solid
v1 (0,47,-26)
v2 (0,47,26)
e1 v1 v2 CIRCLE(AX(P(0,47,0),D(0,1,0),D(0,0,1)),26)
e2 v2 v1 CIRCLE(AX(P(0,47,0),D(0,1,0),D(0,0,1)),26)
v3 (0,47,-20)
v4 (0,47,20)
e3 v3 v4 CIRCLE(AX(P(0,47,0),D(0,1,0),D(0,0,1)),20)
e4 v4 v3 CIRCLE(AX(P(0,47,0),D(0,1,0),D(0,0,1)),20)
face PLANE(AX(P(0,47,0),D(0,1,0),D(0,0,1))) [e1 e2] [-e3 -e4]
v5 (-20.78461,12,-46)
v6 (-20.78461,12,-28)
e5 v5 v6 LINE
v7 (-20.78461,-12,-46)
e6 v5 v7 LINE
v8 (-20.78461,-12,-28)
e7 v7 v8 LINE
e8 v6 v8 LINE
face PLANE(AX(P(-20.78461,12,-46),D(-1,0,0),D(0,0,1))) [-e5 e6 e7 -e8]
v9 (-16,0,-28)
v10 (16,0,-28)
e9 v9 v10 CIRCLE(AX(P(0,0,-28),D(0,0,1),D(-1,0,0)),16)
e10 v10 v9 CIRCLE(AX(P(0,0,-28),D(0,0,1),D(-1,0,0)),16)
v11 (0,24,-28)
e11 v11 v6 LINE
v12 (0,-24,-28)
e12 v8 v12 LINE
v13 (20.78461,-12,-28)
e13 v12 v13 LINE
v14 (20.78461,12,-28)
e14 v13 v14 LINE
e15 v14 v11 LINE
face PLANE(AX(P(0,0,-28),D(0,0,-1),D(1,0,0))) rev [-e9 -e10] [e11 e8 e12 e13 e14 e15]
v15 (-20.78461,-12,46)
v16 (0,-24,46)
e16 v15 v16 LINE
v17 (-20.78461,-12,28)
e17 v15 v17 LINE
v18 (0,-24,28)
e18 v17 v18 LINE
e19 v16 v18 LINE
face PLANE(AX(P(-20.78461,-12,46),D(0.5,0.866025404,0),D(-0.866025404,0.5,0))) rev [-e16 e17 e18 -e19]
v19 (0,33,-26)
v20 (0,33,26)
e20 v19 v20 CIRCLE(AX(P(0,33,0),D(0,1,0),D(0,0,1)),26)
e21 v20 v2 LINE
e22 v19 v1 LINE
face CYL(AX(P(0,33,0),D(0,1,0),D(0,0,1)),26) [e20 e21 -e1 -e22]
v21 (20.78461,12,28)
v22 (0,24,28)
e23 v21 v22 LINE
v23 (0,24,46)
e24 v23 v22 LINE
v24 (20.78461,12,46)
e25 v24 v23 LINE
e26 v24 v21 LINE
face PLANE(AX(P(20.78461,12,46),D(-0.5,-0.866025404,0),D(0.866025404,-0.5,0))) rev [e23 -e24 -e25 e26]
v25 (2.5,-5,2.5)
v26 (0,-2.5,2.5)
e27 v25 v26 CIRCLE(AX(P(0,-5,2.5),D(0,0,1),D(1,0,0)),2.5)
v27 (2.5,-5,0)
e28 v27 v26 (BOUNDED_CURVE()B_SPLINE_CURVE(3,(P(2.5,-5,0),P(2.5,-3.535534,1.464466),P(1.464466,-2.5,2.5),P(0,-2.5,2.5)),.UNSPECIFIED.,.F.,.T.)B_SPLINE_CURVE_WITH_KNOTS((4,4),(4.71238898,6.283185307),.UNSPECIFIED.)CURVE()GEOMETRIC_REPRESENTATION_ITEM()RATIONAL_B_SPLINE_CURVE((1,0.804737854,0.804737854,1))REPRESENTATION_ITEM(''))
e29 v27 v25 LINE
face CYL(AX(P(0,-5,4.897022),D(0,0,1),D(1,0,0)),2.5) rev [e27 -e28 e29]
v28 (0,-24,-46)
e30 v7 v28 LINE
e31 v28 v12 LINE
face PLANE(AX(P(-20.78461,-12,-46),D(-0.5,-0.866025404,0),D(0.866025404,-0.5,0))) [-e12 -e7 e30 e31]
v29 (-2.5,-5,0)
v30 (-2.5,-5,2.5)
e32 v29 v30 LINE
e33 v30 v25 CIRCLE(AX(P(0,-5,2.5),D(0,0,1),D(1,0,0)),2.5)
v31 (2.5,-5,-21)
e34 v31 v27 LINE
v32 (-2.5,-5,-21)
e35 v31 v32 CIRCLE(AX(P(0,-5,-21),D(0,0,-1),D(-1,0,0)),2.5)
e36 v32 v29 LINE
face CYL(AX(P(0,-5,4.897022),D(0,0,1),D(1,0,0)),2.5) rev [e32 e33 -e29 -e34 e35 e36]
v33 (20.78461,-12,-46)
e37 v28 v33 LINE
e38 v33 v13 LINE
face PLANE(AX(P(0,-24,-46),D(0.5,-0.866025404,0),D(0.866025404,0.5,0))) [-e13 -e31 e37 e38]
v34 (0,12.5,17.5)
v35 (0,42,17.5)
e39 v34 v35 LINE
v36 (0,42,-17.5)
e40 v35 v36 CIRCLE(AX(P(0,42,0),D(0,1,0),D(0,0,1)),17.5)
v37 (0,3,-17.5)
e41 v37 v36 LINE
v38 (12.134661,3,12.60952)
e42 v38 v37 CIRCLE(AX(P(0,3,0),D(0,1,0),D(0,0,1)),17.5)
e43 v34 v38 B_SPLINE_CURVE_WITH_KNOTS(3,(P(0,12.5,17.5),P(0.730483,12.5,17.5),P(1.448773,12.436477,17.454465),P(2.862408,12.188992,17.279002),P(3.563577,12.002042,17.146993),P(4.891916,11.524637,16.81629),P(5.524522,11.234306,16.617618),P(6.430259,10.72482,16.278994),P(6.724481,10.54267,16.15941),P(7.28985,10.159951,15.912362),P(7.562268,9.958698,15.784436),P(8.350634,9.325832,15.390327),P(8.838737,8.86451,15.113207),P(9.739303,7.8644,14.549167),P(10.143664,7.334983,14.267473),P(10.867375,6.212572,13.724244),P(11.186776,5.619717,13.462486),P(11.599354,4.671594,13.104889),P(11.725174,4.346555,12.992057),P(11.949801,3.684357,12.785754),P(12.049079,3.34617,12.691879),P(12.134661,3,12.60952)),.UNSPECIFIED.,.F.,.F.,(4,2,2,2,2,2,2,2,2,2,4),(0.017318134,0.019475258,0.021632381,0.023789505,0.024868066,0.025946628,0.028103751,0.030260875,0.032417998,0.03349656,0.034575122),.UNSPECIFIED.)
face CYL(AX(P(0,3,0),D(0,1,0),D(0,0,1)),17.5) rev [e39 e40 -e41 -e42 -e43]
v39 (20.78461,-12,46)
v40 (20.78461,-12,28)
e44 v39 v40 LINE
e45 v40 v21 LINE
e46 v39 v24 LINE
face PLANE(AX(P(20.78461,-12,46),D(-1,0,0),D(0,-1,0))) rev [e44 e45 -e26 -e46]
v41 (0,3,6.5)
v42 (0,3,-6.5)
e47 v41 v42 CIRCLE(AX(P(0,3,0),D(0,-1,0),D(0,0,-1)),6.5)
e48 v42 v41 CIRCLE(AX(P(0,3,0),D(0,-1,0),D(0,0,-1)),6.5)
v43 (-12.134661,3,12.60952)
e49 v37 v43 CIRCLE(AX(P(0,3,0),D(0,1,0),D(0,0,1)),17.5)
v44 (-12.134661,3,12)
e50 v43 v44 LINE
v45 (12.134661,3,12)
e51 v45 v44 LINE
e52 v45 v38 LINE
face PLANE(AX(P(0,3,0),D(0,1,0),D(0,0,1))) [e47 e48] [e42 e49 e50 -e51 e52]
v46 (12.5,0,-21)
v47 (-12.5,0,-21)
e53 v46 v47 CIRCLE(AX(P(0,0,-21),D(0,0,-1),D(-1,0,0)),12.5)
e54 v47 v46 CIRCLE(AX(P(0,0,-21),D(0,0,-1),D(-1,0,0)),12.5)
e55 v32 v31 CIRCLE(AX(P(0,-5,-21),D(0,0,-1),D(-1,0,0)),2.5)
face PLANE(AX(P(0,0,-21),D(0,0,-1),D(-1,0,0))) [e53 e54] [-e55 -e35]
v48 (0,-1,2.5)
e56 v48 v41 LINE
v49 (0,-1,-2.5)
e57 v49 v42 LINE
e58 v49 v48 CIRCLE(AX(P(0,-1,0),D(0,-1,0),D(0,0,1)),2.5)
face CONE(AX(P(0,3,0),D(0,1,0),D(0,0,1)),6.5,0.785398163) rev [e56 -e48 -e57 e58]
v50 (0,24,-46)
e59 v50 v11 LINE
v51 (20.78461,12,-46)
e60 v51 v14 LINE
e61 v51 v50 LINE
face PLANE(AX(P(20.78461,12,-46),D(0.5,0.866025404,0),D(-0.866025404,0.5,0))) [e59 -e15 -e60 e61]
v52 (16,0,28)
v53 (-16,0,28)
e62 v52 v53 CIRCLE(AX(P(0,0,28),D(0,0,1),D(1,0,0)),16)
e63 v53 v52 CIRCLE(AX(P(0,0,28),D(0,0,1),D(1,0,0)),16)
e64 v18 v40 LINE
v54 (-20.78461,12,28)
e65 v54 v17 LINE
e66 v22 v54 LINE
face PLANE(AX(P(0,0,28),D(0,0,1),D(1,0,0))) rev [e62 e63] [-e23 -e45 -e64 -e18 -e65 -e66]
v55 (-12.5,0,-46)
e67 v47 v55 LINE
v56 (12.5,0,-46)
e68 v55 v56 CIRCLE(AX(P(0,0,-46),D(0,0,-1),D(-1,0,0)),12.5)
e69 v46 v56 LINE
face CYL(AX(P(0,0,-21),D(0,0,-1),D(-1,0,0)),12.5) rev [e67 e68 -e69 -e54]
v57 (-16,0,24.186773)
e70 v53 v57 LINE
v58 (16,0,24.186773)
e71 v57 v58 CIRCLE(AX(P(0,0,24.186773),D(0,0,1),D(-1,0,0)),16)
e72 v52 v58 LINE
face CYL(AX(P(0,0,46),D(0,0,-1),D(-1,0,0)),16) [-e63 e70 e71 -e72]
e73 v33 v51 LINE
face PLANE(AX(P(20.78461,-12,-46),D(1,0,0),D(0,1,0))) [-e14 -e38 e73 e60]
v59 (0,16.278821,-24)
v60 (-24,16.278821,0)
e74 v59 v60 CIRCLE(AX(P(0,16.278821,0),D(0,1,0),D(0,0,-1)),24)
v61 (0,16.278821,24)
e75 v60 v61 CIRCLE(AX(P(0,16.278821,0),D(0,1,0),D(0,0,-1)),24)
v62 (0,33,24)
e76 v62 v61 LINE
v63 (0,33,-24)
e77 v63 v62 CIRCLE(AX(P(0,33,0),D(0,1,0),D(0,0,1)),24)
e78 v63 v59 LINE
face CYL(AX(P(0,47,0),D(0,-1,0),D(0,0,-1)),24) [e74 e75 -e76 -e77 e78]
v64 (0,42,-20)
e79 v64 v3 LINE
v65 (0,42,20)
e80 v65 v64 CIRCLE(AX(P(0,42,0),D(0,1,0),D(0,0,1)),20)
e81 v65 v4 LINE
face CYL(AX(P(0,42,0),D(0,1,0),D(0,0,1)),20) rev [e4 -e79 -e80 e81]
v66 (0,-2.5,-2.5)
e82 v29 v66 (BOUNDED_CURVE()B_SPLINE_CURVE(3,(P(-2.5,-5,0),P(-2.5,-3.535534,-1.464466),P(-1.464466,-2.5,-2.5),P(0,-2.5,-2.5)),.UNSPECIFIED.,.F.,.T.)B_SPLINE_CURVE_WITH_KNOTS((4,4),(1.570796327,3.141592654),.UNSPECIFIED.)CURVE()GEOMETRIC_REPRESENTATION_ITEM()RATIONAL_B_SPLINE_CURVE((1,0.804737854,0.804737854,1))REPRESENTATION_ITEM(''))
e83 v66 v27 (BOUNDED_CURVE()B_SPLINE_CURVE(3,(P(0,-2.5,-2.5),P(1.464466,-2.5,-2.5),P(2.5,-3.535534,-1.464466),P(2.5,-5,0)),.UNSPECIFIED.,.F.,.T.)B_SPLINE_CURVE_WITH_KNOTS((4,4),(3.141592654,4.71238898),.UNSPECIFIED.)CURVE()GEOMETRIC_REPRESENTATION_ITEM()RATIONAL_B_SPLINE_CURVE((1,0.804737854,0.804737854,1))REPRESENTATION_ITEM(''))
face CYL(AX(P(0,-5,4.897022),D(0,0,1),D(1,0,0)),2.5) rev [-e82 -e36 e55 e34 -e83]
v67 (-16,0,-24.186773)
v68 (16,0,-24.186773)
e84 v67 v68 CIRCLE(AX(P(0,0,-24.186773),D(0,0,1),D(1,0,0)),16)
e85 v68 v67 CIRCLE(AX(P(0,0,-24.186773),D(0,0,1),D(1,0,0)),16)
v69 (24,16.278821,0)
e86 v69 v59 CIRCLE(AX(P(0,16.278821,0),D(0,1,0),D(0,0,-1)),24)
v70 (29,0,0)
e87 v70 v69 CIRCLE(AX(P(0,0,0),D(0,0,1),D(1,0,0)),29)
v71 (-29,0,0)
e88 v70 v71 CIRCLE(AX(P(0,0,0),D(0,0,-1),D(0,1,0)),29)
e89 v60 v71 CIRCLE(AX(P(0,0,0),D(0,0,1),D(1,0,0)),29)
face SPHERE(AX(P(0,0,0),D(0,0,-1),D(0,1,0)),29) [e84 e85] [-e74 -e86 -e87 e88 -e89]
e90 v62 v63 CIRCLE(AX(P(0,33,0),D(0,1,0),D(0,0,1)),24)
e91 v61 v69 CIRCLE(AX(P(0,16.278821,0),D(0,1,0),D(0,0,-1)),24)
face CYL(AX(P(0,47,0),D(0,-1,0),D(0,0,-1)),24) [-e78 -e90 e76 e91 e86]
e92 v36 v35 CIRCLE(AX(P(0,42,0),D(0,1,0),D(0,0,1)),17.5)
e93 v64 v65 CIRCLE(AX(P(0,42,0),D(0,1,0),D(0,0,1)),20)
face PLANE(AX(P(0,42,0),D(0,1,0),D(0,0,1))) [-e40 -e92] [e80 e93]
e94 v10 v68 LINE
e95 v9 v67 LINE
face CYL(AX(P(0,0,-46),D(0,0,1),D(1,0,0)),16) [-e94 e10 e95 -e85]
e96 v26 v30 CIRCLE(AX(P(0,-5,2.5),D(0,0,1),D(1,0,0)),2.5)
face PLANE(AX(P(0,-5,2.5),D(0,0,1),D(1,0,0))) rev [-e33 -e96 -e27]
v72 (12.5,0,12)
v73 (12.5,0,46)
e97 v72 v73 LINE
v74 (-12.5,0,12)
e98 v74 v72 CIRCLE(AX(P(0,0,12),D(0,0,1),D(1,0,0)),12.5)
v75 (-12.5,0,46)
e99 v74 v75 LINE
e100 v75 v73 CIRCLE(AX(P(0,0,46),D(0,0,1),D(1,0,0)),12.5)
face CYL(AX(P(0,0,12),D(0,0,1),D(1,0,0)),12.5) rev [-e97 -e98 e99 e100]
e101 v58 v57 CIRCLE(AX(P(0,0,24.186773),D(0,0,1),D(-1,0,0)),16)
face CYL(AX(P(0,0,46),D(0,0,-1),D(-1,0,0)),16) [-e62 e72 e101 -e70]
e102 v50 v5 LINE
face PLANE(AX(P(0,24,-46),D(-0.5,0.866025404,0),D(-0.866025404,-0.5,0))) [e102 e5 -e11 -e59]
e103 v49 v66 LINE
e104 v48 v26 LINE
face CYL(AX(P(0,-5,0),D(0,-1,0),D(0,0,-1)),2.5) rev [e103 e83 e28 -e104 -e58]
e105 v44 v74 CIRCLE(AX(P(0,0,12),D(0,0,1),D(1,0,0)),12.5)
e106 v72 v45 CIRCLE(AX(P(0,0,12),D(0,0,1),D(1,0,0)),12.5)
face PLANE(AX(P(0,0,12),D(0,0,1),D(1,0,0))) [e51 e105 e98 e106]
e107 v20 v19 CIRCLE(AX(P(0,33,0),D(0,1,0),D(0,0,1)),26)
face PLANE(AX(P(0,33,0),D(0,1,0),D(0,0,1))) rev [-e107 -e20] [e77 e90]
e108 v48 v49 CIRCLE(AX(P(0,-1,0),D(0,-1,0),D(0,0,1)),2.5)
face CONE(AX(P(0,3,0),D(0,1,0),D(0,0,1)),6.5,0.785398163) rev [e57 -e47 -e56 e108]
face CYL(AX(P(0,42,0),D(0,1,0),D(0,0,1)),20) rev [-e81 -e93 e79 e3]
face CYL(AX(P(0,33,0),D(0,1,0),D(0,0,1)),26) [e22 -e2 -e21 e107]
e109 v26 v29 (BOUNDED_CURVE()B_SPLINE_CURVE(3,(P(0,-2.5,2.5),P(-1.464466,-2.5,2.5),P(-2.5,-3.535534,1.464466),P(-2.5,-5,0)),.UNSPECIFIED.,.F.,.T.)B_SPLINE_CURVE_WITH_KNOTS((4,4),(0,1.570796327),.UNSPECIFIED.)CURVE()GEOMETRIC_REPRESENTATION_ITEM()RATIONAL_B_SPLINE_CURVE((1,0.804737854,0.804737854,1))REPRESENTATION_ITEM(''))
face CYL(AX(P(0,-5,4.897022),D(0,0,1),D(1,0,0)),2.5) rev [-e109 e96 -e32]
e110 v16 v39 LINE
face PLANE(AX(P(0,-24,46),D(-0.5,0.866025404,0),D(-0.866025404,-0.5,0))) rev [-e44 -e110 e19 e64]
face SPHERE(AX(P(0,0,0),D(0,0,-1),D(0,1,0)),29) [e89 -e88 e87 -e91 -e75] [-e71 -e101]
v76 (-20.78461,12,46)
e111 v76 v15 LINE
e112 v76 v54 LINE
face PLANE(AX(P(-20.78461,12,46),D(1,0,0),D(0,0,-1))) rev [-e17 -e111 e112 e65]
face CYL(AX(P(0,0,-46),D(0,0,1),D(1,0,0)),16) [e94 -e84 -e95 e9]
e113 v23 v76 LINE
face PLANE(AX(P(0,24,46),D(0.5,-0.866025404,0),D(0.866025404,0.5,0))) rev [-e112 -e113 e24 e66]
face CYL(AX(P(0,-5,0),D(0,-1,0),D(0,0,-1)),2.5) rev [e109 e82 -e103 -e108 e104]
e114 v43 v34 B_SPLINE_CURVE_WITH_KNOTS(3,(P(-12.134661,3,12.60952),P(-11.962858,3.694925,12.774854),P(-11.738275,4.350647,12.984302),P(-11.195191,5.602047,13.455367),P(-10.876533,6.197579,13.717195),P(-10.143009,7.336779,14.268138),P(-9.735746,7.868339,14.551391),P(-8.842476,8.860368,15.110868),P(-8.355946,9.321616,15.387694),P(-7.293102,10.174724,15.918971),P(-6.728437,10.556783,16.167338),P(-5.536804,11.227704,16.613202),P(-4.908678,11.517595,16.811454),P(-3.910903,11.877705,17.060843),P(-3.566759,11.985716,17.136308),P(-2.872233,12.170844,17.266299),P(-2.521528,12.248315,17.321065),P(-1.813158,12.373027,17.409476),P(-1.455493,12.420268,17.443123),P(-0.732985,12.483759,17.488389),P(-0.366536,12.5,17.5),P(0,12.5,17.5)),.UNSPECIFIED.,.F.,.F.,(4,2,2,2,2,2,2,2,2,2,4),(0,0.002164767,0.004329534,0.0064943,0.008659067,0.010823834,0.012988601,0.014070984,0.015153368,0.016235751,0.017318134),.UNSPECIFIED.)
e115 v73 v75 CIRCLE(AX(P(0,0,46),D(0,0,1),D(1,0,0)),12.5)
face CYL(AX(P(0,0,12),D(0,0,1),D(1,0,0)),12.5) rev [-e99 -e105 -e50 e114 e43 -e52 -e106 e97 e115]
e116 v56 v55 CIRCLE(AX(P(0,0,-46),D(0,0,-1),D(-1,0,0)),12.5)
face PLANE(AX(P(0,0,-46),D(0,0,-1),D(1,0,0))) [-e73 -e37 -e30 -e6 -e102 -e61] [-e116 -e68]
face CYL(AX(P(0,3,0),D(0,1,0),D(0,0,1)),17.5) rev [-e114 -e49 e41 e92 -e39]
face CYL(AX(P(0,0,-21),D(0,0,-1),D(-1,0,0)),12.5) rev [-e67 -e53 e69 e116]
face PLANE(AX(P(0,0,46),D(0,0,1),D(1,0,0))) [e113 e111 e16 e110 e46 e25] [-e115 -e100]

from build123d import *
from build123d.topology import SkipClean

# Parameters (mm, degrees)
SKETCH2_R           = 24
BOSS_EXTRUDE1_DEPTH = 47
SKETCH3_R           = 26
BOSS_EXTRUDE2_DEPTH = 14
SKETCH5_R           = 16
BOSS_EXTRUDE3_DEPTH = 46
BOSS_EXTRUDE4_START = 28
BOSS_EXTRUDE4_DEPTH = 18
SKETCH8_R           = 20
CUT_EXTRUDE1_DEPTH  = 5
SKETCH12_R          = 12.5
CUT_EXTRUDE3_DEPTH  = 34
CUT_EXTRUDE4_START  = -25
SKETCH13_R          = 12.5
CUT_EXTRUDE4_DEPTH  = 25
SKETCH11_R          = 17.5
CUT_EXTRUDE2_DEPTH  = 39
SKETCH16_W          = 29
SKETCH16_H          = 2.5
SKETCH17_W          = 2.5
SKETCH17_H          = 11.435558067


with BuildPart() as part:
    # Sketch1 → Revolve1 (revolve)
    with BuildSketch(Plane.XY):
        with BuildLine():
            Line((-29, 0), (29, 0))
            ThreePointArc((29, 0), (0, 29), (-29, 0))
        make_face()
    revolve(axis=Axis((-1000, 0, 0), (1, 0, 0)))

    # Sketch2 → Boss-Extrude1 (add)
    with BuildSketch(Plane(origin=(0, 0, 0), x_dir=(1, 0, 0), z_dir=(0, 1, 0))):
        with Locations(Location((0, 0, 0), (0, 0, 90))):
            Circle(SKETCH2_R)
    extrude(amount=BOSS_EXTRUDE1_DEPTH)

    # Sketch3 → Boss-Extrude2 (add)
    with BuildSketch(Plane(origin=(0, 47, 0), x_dir=(1, 0, 0), z_dir=(0, 1, 0))):
        with Locations(Location((0, 0, 0), (0, 0, 270))):
            Circle(SKETCH3_R)
    extrude(amount=-BOSS_EXTRUDE2_DEPTH)

    # Sketch5 → Boss-Extrude3 (add)
    with BuildSketch(Plane.XY):
        with Locations(Location((0, 0, 0), (0, 0, 180))):
            Circle(SKETCH5_R)
    boss_extrude3 = extrude(amount=BOSS_EXTRUDE3_DEPTH)

    # Sketch4 → Boss-Extrude4 (add)
    with BuildSketch(Plane.XY.offset(BOSS_EXTRUDE4_START)):
        Polygon((20.784609691, 12), (0, 24), (-20.784609691, 12), (-20.784609691, -12), (0, -24), (20.784609691, -12), align=None)
    boss_extrude4 = extrude(amount=BOSS_EXTRUDE4_DEPTH)

    # Sketch8 → Cut-Extrude1 (cut)
    with BuildSketch(Plane(origin=(0, 47, 0), x_dir=(1, 0, 0), z_dir=(0, 1, 0))):
        with Locations(Location((0, 0, 0), (0, 0, 270))):
            Circle(SKETCH8_R)
    extrude(amount=-CUT_EXTRUDE1_DEPTH, mode=Mode.SUBTRACT)

    # Sketch12 → Cut-Extrude3 (cut)
    with BuildSketch(Plane.XY.offset(46)):
        Circle(SKETCH12_R)
    extrude(amount=-CUT_EXTRUDE3_DEPTH, mode=Mode.SUBTRACT)

    # Mirror1: Boss-Extrude3, Boss-Extrude4 across plane
    add(boss_extrude3.mirror(Plane.XY))
    add(boss_extrude4.mirror(Plane.XY))

    # Sketch13 → Cut-Extrude4 (cut)
    with BuildSketch(Plane(origin=(0, 0, -46), x_dir=(-1, 0, 0), z_dir=(0, 0, -1)).offset(CUT_EXTRUDE4_START)):
        with Locations(Location((0, 0, 0), (0, 0, 180))):
            Circle(SKETCH13_R)
    extrude(amount=CUT_EXTRUDE4_DEPTH, mode=Mode.SUBTRACT)

    # Sketch11 → Cut-Extrude2 (cut)
    with BuildSketch(Plane(origin=(0, 42, 0), x_dir=(1, 0, 0), z_dir=(0, 1, 0))):
        with Locations(Location((0, 0, 0), (0, 0, 270))):
            Circle(SKETCH11_R)
    extrude(amount=-CUT_EXTRUDE2_DEPTH, mode=Mode.SUBTRACT)

    # Sketch15 → Cut-Revolve1 (revolve, cut)
    with BuildSketch(Plane(origin=(0, 0, 0), x_dir=(0, 0, -1), z_dir=(1, 0, 0))):
        Polygon((-6.5, 3), (0, -3.5), (0, 11), (-6.5, 11), align=None)
    revolve(axis=Axis((0, -1000, 0), (0, 1, 0)), mode=Mode.SUBTRACT)

    # Sketch16 → Cut-Revolve2 (revolve, cut)
    with BuildSketch(Plane(origin=(0, 0, 0), x_dir=(0, 0, -1), z_dir=(1, 0, 0)), mode=Mode.PRIVATE) as cut_revolve2_sk:
        with Locations((12, -6.25)):
            Rectangle(SKETCH16_W, SKETCH16_H)
    revolve(cut_revolve2_sk.sketch.rotate(Axis((0, -5, 4.897022233), (0, 0, -1)), 270), axis=Axis((0, -5, 4.897022233), (0, 0, -1)), mode=Mode.SUBTRACT)

    # Sketch17 → Cut-Revolve3 (revolve, cut)
    with SkipClean():  # the faces are left unmerged after this step: merging them gives an invalid solid
        with BuildSketch(Plane(origin=(0, 0, 0), x_dir=(0, 0, -1), z_dir=(1, 0, 0))):
            with Locations((-1.25, 0.717779034)):
                Rectangle(SKETCH17_W, SKETCH17_H)
        revolve(axis=Axis((0, -5, 0), (0, 1, 0)), mode=Mode.SUBTRACT)


solid = part.part
